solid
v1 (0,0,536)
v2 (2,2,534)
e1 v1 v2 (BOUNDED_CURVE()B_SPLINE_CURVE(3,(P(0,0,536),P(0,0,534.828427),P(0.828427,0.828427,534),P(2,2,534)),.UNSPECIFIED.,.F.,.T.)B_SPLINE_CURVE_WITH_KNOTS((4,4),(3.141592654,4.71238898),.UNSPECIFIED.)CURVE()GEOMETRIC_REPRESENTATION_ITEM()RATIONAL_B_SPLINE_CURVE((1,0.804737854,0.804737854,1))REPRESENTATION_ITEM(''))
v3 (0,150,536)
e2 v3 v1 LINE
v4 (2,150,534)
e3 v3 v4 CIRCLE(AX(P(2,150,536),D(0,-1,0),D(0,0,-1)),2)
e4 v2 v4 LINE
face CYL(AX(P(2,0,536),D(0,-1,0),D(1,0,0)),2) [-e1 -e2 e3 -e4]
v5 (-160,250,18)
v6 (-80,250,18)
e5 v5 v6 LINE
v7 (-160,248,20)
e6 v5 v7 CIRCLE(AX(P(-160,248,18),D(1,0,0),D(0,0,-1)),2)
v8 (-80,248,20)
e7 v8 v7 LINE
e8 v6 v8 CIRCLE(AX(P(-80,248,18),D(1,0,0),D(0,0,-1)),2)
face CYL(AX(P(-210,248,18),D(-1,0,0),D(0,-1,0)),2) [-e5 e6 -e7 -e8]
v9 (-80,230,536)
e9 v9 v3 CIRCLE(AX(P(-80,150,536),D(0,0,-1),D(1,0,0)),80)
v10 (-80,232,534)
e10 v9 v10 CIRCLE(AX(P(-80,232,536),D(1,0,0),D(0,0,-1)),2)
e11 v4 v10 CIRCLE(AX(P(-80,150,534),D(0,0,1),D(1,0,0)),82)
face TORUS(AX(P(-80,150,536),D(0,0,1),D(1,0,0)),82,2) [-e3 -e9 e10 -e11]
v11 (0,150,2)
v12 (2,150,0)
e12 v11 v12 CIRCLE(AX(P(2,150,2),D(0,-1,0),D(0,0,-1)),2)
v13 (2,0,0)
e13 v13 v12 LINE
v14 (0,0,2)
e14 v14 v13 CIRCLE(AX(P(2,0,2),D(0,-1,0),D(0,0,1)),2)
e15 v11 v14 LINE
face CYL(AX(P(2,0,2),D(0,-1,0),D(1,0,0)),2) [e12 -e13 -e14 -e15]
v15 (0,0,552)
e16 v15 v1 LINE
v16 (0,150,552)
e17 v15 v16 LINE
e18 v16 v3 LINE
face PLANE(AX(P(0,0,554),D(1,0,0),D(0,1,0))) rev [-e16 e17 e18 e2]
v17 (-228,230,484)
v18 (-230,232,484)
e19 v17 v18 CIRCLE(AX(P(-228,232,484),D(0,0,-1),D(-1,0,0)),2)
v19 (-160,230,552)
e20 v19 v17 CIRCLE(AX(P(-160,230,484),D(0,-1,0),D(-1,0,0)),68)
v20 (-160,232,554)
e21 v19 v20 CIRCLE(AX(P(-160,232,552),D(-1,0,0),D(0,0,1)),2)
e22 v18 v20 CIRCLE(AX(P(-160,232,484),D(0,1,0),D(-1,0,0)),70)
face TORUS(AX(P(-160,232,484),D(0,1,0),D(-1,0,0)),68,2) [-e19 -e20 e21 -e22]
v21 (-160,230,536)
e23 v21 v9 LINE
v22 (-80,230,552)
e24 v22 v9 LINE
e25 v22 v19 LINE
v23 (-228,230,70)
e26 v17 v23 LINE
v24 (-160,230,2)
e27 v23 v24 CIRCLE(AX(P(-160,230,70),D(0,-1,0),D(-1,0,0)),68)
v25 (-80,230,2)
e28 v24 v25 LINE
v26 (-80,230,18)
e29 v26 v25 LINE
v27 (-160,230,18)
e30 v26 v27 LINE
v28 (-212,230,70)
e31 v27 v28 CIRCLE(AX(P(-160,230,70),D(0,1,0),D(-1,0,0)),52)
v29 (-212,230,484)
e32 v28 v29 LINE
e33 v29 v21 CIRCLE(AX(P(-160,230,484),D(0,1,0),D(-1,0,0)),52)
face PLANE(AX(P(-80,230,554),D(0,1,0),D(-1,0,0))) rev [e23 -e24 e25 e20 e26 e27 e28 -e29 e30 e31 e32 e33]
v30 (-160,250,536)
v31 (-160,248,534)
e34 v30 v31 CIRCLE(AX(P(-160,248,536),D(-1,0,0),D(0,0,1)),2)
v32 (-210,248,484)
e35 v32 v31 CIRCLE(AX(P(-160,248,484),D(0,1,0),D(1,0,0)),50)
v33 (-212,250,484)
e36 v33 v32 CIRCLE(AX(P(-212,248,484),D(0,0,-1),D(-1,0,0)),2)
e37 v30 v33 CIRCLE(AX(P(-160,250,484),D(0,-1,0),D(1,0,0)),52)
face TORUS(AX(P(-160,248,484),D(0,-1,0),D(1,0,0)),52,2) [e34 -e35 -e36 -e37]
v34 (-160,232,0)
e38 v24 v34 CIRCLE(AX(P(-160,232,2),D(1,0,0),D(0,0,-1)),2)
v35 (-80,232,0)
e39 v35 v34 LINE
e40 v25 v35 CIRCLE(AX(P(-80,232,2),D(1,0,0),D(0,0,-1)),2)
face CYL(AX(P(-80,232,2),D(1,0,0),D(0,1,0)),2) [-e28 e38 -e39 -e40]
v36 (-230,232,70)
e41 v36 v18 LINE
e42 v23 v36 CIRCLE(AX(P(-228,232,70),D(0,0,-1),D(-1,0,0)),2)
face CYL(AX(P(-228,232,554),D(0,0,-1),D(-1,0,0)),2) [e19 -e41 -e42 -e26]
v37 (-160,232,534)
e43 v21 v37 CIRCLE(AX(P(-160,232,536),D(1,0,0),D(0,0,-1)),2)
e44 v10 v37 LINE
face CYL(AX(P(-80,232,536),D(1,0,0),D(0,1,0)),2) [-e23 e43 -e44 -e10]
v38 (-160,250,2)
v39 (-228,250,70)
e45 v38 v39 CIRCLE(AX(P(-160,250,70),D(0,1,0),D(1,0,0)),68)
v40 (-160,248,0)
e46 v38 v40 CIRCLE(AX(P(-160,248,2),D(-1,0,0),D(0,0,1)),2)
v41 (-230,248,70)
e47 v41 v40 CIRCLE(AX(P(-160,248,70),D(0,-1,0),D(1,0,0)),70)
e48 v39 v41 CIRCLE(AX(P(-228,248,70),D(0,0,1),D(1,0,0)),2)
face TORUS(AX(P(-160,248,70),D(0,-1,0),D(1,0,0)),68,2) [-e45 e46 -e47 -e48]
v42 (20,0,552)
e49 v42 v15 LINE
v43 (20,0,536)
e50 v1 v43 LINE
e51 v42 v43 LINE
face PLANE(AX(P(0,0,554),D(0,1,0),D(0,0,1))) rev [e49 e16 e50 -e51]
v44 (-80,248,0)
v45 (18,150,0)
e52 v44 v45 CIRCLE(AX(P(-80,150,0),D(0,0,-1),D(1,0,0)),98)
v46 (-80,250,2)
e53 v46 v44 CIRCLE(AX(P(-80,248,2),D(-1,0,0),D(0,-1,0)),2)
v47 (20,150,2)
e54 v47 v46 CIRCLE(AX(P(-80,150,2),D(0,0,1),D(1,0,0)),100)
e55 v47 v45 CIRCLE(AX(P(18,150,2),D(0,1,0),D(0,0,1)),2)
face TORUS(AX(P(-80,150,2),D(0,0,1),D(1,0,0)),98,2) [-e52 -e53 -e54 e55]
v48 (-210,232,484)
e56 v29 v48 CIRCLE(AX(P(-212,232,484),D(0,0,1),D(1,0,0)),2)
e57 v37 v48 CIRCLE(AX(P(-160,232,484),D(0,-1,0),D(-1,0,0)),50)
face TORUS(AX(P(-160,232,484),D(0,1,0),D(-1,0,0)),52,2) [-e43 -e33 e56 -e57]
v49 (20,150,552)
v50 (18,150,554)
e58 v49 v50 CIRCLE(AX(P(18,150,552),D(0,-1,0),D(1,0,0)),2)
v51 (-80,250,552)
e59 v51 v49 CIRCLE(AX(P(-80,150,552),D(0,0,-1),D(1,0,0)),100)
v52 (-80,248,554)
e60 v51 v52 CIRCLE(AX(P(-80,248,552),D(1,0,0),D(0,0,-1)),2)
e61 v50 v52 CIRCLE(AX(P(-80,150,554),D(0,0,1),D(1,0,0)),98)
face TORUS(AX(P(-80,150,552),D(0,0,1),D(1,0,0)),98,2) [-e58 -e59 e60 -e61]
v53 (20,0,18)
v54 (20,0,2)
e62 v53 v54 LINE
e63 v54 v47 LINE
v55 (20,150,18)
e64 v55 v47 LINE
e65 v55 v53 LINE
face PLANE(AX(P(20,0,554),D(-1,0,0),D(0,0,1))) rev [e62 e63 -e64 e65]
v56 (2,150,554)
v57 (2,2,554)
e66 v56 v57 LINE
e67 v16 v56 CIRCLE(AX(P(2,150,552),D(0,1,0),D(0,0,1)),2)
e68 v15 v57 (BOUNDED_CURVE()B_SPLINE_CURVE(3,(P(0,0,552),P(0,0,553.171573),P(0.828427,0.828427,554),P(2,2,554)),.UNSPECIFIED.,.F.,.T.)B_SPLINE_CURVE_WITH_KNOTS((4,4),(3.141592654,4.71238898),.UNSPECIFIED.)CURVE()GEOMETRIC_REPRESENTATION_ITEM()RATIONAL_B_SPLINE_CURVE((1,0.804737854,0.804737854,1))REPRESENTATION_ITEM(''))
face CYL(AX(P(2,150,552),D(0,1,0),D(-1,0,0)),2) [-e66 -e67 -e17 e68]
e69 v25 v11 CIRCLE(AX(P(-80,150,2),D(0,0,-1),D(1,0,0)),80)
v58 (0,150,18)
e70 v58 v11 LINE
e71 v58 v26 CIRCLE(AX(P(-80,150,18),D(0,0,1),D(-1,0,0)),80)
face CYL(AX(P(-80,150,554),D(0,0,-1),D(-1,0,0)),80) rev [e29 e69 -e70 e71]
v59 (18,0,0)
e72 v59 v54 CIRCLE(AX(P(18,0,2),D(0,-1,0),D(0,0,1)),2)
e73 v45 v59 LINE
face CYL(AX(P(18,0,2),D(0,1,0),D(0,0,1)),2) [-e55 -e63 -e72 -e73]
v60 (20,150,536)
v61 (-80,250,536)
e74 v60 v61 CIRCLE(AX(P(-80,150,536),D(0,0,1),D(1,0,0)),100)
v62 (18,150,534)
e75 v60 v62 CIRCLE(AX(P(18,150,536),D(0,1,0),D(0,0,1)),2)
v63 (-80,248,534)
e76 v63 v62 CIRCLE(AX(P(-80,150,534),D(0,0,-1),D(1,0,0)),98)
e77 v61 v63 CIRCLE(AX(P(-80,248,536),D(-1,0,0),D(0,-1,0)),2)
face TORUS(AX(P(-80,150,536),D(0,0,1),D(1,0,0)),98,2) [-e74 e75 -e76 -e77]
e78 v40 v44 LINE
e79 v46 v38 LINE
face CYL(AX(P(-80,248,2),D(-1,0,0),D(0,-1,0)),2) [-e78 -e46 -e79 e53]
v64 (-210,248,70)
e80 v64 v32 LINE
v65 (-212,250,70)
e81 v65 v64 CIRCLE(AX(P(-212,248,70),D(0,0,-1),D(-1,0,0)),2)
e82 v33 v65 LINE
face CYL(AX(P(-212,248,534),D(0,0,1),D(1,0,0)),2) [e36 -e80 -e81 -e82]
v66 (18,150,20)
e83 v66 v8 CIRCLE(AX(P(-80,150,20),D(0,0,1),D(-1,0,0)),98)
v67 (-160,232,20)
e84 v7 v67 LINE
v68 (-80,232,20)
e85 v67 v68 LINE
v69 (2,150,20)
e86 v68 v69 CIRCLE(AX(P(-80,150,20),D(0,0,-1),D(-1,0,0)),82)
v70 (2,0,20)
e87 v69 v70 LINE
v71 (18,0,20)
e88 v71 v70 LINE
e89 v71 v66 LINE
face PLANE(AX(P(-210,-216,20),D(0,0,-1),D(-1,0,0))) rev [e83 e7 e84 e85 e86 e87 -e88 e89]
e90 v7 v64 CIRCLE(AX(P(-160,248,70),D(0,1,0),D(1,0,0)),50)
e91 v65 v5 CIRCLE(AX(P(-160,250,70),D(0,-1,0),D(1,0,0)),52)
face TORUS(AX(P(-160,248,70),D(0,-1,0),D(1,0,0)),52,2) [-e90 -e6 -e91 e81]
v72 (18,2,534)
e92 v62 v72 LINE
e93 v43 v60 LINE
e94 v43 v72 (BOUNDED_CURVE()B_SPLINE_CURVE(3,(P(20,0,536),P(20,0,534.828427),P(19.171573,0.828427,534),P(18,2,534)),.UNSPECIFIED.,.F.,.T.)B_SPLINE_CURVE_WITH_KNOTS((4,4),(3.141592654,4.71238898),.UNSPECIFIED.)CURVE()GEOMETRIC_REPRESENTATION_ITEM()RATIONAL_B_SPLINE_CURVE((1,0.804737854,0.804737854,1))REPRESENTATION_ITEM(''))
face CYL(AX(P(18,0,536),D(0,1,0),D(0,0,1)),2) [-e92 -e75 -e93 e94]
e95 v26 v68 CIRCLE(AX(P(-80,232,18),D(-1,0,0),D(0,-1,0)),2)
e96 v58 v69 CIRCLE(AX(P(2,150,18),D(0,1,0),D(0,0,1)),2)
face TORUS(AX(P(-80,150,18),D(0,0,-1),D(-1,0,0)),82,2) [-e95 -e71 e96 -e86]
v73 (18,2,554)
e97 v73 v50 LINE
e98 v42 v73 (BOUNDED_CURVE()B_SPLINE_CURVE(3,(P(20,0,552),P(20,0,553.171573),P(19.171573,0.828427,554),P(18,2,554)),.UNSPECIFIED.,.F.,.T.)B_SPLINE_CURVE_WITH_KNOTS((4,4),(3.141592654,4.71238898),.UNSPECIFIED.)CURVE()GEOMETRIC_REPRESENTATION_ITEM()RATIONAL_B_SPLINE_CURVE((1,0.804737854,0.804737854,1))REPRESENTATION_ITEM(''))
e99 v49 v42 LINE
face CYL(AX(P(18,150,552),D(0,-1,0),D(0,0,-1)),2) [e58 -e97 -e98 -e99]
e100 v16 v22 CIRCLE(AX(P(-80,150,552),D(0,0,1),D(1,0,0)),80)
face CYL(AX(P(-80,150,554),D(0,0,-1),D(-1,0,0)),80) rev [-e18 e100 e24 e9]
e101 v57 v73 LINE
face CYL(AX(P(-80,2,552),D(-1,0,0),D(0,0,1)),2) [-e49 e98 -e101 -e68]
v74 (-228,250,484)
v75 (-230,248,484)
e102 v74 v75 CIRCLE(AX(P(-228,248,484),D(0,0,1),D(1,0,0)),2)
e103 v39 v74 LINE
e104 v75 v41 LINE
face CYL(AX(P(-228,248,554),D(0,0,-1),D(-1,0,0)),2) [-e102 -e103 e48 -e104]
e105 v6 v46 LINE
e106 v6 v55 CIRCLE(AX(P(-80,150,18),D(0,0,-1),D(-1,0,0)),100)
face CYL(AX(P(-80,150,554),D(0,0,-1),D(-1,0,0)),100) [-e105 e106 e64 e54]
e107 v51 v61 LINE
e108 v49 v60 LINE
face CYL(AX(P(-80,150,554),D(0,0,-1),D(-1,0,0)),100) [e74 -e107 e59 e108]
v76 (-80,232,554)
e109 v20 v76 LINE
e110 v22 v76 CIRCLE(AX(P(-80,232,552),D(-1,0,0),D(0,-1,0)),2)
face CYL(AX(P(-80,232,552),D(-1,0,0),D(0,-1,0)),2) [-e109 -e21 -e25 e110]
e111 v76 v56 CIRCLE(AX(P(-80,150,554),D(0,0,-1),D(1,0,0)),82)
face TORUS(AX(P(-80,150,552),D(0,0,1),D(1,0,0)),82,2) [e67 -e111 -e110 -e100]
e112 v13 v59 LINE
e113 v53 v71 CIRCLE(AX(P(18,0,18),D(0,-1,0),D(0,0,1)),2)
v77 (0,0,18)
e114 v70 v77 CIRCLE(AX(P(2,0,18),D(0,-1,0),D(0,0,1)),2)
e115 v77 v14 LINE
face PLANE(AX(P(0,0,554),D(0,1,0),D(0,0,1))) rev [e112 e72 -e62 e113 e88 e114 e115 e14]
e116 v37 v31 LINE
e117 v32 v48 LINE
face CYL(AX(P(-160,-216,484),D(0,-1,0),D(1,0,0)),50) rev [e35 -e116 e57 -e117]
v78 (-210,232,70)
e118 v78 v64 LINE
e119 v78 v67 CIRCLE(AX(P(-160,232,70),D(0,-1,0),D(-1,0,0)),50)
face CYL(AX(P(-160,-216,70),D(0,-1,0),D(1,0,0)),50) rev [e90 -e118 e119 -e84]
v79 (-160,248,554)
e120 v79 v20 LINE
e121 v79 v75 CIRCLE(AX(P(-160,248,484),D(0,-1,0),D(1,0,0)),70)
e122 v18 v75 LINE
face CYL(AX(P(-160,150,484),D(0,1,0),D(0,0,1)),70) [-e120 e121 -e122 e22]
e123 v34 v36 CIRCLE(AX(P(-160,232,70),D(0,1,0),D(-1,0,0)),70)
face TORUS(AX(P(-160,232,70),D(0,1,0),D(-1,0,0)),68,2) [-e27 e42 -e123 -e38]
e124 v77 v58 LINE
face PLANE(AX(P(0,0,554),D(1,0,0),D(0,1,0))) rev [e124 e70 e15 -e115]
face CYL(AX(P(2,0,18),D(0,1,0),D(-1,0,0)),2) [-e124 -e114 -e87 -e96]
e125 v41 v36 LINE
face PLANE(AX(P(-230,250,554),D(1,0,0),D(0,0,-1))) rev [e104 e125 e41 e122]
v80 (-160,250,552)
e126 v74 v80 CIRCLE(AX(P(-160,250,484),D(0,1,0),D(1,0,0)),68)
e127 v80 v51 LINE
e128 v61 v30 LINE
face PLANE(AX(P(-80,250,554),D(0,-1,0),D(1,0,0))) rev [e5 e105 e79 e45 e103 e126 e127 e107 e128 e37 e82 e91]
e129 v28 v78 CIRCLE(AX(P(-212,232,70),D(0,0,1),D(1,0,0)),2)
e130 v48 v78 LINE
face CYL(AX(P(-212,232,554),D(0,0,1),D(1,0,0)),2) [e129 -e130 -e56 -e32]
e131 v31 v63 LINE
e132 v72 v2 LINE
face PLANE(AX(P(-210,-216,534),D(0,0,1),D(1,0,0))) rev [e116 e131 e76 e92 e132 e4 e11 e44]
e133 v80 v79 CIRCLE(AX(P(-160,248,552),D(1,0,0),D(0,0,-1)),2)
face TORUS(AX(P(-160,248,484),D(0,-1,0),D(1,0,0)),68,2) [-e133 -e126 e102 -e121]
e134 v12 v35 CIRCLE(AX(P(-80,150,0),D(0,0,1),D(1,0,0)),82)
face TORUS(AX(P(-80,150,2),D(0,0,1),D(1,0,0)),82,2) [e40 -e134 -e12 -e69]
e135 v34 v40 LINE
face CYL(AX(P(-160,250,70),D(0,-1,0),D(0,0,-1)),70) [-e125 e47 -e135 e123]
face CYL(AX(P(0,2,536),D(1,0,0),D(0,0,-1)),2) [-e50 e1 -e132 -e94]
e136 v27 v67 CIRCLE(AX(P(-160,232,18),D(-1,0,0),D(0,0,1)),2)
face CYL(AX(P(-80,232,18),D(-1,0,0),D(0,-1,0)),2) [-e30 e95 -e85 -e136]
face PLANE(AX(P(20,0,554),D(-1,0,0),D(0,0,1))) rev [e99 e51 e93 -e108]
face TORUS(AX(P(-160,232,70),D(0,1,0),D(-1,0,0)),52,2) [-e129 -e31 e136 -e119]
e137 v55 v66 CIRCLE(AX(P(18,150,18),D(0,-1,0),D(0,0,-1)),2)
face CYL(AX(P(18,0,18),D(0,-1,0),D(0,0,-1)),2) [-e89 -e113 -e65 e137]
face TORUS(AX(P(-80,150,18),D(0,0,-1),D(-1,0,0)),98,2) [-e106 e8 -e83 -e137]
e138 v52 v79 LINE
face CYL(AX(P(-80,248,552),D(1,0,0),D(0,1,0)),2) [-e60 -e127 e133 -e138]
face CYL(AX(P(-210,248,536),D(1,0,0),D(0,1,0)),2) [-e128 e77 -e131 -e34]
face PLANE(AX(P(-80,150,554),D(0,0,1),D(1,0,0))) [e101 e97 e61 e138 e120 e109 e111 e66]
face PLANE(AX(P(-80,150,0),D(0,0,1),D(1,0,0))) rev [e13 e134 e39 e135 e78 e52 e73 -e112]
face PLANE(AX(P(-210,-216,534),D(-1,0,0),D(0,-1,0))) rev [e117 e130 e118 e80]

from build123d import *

# Parameters (mm, degrees)
BOSS_EXTRUDE1_DEPTH = 554
SKETCH2_W           = 357.128489267
SKETCH2_H           = 514
CUT_EXTRUDE1_DEPTH  = 466
FILLET1_R           = 50
FILLET2_R           = 70
FILLET3_R           = 2


with BuildPart() as part:
    # Sketch1 → Boss-Extrude1 (new body)
    with BuildSketch(Plane.XY):
        with BuildLine():
            Line((0, 0), (0, 150))
            ThreePointArc((0, 150), (-23.431457505, 206.568542495), (-80, 230))
            Line((-80, 230), (-230, 230))
            Line((-230, 230), (-230, 250))
            Line((-230, 250), (-80, 250))
            ThreePointArc((-80, 250), (-9.289321881, 220.710678119), (20, 150))
            Line((20, 150), (20, 0))
            Line((20, 0), (0, 0))
        make_face()
    extrude(amount=BOSS_EXTRUDE1_DEPTH)

    # Sketch2 → Cut-Extrude1 (cut)
    with BuildSketch(Plane(origin=(0, 250, 0), x_dir=(1, 0, 0), z_dir=(0, 1, 0))):
        with Locations((-31.435755366, -277)):
            Rectangle(SKETCH2_W, SKETCH2_H)
    extrude(amount=-CUT_EXTRUDE1_DEPTH, mode=Mode.SUBTRACT)

    # Fillet1
    fillet1_edges = [part.edges().sort_by_distance(p)[0] for p in [
        (-210, 240, 534),
        (-210, 240, 20),
    ]]
    fillet(fillet1_edges, radius=FILLET1_R)

    # Fillet2
    fillet2_edges = [part.edges().sort_by_distance(p)[0] for p in [
        (-230, 240, 554),
        (-230, 240, 0),
    ]]
    fillet(fillet2_edges, radius=FILLET2_R)

    # Fillet3
    fillet3_edges = [part.edges().sort_by_distance(p)[0] for p in [
        (-9.289321881, 220.710678119, 554),
        (20, 75, 0),
        (-120, 250, 554),
        (-23.431457505, 206.568542495, 554),
        (0, 75, 554),
        (0, 75, 534),
        (0, 75, 20),
        (-9.289321881, 220.710678119, 20),
        (20, 75, 20),
        (-23.431457505, 206.568542495, 20),
        (-120, 230, 20),
        (20, 75, 534),
        (-9.289321881, 220.710678119, 534),
        (-23.431457505, 206.568542495, 534),
        (10, 0, 534),
        (10, 0, 554),
        (-120, 250, 20),
        (-210, 250, 277),
        (-210, 230, 277),
        (-120, 230, 534),
        (-120, 250, 534),
        (-195.355339059, 250, 34.644660941),
        (-195.355339059, 230, 34.644660941),
        (-195.355339059, 250, 519.355339059),
        (-195.355339059, 230, 519.355339059),
        (-230, 230, 277),
        (-230, 250, 277),
        (20, 75, 554),
        (-120, 230, 554),
        (-120, 230, 0),
        (-209.497474683, 230, 533.497474683),
        (-209.497474683, 230, 20.502525317),
        (-209.497474683, 250, 533.497474683),
        (-209.497474683, 250, 20.502525317),
        (0, 75, 0),
        (-23.431457505, 206.568542495, 0),
        (-120, 250, 0),
        (-9.289321881, 220.710678119, 0),
    ]]
    fillet(fillet3_edges, radius=FILLET3_R)


solid = part.part
